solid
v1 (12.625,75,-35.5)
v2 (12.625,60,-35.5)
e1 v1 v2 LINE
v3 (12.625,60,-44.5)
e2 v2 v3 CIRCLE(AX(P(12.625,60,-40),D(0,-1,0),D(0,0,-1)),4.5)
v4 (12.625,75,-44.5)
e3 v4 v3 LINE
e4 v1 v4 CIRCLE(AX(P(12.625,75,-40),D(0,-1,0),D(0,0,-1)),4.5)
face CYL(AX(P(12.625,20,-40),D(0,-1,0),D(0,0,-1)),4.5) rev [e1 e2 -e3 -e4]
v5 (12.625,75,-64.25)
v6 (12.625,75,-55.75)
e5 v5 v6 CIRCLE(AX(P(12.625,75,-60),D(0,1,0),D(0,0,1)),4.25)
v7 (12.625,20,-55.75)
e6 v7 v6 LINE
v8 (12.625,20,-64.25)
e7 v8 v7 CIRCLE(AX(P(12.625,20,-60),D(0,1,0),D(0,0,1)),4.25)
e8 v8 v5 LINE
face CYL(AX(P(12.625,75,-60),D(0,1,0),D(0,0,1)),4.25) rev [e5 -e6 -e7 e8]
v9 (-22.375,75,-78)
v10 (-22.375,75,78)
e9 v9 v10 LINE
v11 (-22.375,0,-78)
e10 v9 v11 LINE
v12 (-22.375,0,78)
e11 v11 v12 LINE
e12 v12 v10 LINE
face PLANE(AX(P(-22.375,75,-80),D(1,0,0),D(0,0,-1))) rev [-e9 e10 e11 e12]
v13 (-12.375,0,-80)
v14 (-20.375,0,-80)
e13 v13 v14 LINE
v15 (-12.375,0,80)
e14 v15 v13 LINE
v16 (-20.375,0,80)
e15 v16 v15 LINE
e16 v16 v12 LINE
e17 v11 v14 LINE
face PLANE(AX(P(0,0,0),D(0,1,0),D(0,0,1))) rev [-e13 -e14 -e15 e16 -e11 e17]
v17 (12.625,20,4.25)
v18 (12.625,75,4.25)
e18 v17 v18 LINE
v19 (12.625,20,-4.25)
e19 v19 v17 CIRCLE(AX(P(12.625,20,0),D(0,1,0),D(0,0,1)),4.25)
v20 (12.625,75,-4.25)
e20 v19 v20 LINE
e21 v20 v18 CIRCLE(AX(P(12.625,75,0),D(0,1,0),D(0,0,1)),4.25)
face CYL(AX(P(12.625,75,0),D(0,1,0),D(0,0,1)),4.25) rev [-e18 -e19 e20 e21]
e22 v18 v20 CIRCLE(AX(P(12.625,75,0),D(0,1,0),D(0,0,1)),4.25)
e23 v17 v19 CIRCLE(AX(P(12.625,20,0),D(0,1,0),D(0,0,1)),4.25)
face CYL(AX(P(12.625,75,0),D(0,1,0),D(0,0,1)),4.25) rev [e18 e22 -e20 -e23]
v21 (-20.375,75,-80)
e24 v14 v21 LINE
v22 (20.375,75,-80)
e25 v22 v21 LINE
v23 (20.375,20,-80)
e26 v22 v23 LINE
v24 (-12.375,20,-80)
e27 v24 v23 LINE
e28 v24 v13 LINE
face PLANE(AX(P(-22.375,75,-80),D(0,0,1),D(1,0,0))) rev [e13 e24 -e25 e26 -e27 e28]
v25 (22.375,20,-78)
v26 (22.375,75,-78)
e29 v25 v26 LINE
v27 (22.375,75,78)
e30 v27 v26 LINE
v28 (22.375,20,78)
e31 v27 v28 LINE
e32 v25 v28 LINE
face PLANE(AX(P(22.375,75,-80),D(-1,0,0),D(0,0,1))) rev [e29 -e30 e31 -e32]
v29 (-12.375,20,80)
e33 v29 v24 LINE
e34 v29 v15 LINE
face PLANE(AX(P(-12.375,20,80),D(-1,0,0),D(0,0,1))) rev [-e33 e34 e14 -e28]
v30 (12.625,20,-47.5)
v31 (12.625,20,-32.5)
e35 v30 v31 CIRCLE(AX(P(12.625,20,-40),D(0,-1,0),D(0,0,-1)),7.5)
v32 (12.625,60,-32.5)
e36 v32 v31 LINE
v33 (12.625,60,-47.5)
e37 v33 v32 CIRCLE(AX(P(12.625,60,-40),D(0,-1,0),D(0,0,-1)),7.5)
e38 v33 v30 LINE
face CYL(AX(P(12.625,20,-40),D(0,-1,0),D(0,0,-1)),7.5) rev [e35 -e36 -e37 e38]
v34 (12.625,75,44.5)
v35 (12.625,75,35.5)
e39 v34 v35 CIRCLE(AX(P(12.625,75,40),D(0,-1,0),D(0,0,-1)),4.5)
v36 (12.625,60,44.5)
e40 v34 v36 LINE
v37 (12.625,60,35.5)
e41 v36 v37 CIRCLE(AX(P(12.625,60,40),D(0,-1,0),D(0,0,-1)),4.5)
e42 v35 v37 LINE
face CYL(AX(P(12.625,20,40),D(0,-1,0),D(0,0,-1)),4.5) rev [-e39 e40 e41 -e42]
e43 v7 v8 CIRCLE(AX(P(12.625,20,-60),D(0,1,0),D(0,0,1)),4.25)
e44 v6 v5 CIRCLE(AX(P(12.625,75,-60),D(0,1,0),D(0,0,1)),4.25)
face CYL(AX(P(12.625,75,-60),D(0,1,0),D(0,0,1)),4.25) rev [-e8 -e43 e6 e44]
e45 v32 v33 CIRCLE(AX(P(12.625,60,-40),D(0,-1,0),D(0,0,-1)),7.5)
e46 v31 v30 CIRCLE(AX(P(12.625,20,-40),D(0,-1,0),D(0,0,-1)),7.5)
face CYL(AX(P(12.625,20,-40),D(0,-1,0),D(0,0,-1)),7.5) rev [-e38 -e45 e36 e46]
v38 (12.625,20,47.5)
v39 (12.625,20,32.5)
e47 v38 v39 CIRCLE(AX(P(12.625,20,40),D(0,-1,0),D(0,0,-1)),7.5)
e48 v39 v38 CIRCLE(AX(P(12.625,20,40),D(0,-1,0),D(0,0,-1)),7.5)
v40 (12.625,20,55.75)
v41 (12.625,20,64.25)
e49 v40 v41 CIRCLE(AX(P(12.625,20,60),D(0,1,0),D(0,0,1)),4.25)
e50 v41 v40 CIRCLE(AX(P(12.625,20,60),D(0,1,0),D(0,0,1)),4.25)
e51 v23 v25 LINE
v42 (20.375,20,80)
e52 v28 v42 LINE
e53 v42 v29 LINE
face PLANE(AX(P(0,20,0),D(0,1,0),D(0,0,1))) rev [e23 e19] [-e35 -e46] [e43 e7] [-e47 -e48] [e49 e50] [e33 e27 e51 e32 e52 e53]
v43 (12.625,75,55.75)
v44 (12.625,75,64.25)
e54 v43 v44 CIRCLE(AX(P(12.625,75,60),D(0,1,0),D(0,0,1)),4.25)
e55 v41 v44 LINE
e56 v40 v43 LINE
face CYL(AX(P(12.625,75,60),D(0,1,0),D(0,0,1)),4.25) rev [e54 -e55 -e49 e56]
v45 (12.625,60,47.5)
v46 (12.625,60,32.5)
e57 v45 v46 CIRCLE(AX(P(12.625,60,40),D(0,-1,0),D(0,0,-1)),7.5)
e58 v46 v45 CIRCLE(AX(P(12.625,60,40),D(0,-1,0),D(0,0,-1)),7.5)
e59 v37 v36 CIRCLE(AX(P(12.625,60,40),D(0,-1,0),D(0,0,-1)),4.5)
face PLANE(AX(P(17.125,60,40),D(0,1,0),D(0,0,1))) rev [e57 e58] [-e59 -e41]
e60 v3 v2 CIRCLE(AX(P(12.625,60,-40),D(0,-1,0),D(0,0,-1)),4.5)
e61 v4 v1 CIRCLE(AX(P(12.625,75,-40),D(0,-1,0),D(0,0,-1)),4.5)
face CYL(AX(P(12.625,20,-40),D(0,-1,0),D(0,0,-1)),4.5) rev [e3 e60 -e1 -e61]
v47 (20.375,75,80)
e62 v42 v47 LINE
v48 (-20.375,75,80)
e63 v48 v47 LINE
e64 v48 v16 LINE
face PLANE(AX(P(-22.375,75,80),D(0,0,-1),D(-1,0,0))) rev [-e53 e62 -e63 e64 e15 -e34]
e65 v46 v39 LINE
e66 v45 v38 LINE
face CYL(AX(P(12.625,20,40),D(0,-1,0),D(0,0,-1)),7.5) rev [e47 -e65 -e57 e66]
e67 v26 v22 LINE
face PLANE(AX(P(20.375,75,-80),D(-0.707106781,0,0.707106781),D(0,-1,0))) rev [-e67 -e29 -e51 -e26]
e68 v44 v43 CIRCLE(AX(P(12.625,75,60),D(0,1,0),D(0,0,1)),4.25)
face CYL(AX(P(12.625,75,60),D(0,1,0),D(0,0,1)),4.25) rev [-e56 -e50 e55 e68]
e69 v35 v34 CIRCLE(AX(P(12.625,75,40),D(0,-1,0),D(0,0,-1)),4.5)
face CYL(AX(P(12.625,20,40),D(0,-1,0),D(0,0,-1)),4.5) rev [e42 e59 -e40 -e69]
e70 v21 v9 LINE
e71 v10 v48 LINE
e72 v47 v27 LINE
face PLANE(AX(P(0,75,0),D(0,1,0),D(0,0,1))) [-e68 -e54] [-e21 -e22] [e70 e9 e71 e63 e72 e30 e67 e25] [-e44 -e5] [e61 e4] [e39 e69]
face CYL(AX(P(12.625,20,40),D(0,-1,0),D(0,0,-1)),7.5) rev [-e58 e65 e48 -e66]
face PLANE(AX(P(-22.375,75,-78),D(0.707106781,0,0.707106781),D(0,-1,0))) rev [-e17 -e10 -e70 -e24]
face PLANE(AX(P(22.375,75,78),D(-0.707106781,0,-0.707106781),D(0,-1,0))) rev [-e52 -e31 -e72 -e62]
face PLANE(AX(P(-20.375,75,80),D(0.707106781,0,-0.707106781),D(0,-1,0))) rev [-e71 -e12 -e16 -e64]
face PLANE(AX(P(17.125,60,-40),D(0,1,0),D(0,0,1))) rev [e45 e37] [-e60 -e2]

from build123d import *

# Parameters (mm, degrees)
SKETCH1_W                                           = 44.75
SKETCH1_H                                           = 160
BOSS_EXTRUDE1_DEPTH                                 = 75
SKETCH5_W                                           = 34.75
SKETCH5_H                                           = 160
CUT_EXTRUDE3_DEPTH                                  = 20
F_8_5_8_5_DIAMETER_HOLE1_D                          = 8.5
CHAMFER2_SIZE                                       = 2
CBORE_FOR_M8_HEX_SOCKET_HEAD_CAP_SCREW1_D           = 9
CBORE_FOR_M8_HEX_SOCKET_HEAD_CAP_SCREW1_CBORE_D     = 15
CBORE_FOR_M8_HEX_SOCKET_HEAD_CAP_SCREW1_CBORE_DEPTH = 40


with BuildPart() as part:
    # Sketch1 → Boss-Extrude1 (new body)
    with BuildSketch(Plane(origin=(0, 0, 0), x_dir=(1, 0, 0), z_dir=(0, 1, 0))):
        Rectangle(SKETCH1_W, SKETCH1_H)
    extrude(amount=BOSS_EXTRUDE1_DEPTH)

    # Sketch5 → Cut-Extrude3 (cut)
    with BuildSketch(Plane.XZ):
        with Locations((5, 0)):
            Rectangle(SKETCH5_W, SKETCH5_H)
    extrude(amount=-CUT_EXTRUDE3_DEPTH, mode=Mode.SUBTRACT)

    # Ø8.5 (8.5) Diameter Hole1 (through all)
    with Locations(Plane(origin=(0, 75, 0), x_dir=(-1, 0, 0), z_dir=(0, 1, 0))):
        with Locations((-12.625, -60), (-12.625, 0), (-12.625, 60)):
            Hole(F_8_5_8_5_DIAMETER_HOLE1_D / 2)

    # Chamfer2
    chamfer2_edges = [part.edges().sort_by_distance(p)[0] for p in [
        (22.375, 47.5, 80),
        (-22.375, 37.5, 80),
        (-22.375, 37.5, -80),
        (22.375, 47.5, -80),
    ]]
    chamfer(chamfer2_edges, length=CHAMFER2_SIZE)

    # CBORE for M8 Hex Socket Head Cap Screw1 (through all)
    with Locations(Plane.XZ.offset(-20)):
        with Locations((12.625, 40), (12.625, -40)):
            CounterBoreHole(CBORE_FOR_M8_HEX_SOCKET_HEAD_CAP_SCREW1_D / 2, CBORE_FOR_M8_HEX_SOCKET_HEAD_CAP_SCREW1_CBORE_D / 2, CBORE_FOR_M8_HEX_SOCKET_HEAD_CAP_SCREW1_CBORE_DEPTH)


solid = part.part
